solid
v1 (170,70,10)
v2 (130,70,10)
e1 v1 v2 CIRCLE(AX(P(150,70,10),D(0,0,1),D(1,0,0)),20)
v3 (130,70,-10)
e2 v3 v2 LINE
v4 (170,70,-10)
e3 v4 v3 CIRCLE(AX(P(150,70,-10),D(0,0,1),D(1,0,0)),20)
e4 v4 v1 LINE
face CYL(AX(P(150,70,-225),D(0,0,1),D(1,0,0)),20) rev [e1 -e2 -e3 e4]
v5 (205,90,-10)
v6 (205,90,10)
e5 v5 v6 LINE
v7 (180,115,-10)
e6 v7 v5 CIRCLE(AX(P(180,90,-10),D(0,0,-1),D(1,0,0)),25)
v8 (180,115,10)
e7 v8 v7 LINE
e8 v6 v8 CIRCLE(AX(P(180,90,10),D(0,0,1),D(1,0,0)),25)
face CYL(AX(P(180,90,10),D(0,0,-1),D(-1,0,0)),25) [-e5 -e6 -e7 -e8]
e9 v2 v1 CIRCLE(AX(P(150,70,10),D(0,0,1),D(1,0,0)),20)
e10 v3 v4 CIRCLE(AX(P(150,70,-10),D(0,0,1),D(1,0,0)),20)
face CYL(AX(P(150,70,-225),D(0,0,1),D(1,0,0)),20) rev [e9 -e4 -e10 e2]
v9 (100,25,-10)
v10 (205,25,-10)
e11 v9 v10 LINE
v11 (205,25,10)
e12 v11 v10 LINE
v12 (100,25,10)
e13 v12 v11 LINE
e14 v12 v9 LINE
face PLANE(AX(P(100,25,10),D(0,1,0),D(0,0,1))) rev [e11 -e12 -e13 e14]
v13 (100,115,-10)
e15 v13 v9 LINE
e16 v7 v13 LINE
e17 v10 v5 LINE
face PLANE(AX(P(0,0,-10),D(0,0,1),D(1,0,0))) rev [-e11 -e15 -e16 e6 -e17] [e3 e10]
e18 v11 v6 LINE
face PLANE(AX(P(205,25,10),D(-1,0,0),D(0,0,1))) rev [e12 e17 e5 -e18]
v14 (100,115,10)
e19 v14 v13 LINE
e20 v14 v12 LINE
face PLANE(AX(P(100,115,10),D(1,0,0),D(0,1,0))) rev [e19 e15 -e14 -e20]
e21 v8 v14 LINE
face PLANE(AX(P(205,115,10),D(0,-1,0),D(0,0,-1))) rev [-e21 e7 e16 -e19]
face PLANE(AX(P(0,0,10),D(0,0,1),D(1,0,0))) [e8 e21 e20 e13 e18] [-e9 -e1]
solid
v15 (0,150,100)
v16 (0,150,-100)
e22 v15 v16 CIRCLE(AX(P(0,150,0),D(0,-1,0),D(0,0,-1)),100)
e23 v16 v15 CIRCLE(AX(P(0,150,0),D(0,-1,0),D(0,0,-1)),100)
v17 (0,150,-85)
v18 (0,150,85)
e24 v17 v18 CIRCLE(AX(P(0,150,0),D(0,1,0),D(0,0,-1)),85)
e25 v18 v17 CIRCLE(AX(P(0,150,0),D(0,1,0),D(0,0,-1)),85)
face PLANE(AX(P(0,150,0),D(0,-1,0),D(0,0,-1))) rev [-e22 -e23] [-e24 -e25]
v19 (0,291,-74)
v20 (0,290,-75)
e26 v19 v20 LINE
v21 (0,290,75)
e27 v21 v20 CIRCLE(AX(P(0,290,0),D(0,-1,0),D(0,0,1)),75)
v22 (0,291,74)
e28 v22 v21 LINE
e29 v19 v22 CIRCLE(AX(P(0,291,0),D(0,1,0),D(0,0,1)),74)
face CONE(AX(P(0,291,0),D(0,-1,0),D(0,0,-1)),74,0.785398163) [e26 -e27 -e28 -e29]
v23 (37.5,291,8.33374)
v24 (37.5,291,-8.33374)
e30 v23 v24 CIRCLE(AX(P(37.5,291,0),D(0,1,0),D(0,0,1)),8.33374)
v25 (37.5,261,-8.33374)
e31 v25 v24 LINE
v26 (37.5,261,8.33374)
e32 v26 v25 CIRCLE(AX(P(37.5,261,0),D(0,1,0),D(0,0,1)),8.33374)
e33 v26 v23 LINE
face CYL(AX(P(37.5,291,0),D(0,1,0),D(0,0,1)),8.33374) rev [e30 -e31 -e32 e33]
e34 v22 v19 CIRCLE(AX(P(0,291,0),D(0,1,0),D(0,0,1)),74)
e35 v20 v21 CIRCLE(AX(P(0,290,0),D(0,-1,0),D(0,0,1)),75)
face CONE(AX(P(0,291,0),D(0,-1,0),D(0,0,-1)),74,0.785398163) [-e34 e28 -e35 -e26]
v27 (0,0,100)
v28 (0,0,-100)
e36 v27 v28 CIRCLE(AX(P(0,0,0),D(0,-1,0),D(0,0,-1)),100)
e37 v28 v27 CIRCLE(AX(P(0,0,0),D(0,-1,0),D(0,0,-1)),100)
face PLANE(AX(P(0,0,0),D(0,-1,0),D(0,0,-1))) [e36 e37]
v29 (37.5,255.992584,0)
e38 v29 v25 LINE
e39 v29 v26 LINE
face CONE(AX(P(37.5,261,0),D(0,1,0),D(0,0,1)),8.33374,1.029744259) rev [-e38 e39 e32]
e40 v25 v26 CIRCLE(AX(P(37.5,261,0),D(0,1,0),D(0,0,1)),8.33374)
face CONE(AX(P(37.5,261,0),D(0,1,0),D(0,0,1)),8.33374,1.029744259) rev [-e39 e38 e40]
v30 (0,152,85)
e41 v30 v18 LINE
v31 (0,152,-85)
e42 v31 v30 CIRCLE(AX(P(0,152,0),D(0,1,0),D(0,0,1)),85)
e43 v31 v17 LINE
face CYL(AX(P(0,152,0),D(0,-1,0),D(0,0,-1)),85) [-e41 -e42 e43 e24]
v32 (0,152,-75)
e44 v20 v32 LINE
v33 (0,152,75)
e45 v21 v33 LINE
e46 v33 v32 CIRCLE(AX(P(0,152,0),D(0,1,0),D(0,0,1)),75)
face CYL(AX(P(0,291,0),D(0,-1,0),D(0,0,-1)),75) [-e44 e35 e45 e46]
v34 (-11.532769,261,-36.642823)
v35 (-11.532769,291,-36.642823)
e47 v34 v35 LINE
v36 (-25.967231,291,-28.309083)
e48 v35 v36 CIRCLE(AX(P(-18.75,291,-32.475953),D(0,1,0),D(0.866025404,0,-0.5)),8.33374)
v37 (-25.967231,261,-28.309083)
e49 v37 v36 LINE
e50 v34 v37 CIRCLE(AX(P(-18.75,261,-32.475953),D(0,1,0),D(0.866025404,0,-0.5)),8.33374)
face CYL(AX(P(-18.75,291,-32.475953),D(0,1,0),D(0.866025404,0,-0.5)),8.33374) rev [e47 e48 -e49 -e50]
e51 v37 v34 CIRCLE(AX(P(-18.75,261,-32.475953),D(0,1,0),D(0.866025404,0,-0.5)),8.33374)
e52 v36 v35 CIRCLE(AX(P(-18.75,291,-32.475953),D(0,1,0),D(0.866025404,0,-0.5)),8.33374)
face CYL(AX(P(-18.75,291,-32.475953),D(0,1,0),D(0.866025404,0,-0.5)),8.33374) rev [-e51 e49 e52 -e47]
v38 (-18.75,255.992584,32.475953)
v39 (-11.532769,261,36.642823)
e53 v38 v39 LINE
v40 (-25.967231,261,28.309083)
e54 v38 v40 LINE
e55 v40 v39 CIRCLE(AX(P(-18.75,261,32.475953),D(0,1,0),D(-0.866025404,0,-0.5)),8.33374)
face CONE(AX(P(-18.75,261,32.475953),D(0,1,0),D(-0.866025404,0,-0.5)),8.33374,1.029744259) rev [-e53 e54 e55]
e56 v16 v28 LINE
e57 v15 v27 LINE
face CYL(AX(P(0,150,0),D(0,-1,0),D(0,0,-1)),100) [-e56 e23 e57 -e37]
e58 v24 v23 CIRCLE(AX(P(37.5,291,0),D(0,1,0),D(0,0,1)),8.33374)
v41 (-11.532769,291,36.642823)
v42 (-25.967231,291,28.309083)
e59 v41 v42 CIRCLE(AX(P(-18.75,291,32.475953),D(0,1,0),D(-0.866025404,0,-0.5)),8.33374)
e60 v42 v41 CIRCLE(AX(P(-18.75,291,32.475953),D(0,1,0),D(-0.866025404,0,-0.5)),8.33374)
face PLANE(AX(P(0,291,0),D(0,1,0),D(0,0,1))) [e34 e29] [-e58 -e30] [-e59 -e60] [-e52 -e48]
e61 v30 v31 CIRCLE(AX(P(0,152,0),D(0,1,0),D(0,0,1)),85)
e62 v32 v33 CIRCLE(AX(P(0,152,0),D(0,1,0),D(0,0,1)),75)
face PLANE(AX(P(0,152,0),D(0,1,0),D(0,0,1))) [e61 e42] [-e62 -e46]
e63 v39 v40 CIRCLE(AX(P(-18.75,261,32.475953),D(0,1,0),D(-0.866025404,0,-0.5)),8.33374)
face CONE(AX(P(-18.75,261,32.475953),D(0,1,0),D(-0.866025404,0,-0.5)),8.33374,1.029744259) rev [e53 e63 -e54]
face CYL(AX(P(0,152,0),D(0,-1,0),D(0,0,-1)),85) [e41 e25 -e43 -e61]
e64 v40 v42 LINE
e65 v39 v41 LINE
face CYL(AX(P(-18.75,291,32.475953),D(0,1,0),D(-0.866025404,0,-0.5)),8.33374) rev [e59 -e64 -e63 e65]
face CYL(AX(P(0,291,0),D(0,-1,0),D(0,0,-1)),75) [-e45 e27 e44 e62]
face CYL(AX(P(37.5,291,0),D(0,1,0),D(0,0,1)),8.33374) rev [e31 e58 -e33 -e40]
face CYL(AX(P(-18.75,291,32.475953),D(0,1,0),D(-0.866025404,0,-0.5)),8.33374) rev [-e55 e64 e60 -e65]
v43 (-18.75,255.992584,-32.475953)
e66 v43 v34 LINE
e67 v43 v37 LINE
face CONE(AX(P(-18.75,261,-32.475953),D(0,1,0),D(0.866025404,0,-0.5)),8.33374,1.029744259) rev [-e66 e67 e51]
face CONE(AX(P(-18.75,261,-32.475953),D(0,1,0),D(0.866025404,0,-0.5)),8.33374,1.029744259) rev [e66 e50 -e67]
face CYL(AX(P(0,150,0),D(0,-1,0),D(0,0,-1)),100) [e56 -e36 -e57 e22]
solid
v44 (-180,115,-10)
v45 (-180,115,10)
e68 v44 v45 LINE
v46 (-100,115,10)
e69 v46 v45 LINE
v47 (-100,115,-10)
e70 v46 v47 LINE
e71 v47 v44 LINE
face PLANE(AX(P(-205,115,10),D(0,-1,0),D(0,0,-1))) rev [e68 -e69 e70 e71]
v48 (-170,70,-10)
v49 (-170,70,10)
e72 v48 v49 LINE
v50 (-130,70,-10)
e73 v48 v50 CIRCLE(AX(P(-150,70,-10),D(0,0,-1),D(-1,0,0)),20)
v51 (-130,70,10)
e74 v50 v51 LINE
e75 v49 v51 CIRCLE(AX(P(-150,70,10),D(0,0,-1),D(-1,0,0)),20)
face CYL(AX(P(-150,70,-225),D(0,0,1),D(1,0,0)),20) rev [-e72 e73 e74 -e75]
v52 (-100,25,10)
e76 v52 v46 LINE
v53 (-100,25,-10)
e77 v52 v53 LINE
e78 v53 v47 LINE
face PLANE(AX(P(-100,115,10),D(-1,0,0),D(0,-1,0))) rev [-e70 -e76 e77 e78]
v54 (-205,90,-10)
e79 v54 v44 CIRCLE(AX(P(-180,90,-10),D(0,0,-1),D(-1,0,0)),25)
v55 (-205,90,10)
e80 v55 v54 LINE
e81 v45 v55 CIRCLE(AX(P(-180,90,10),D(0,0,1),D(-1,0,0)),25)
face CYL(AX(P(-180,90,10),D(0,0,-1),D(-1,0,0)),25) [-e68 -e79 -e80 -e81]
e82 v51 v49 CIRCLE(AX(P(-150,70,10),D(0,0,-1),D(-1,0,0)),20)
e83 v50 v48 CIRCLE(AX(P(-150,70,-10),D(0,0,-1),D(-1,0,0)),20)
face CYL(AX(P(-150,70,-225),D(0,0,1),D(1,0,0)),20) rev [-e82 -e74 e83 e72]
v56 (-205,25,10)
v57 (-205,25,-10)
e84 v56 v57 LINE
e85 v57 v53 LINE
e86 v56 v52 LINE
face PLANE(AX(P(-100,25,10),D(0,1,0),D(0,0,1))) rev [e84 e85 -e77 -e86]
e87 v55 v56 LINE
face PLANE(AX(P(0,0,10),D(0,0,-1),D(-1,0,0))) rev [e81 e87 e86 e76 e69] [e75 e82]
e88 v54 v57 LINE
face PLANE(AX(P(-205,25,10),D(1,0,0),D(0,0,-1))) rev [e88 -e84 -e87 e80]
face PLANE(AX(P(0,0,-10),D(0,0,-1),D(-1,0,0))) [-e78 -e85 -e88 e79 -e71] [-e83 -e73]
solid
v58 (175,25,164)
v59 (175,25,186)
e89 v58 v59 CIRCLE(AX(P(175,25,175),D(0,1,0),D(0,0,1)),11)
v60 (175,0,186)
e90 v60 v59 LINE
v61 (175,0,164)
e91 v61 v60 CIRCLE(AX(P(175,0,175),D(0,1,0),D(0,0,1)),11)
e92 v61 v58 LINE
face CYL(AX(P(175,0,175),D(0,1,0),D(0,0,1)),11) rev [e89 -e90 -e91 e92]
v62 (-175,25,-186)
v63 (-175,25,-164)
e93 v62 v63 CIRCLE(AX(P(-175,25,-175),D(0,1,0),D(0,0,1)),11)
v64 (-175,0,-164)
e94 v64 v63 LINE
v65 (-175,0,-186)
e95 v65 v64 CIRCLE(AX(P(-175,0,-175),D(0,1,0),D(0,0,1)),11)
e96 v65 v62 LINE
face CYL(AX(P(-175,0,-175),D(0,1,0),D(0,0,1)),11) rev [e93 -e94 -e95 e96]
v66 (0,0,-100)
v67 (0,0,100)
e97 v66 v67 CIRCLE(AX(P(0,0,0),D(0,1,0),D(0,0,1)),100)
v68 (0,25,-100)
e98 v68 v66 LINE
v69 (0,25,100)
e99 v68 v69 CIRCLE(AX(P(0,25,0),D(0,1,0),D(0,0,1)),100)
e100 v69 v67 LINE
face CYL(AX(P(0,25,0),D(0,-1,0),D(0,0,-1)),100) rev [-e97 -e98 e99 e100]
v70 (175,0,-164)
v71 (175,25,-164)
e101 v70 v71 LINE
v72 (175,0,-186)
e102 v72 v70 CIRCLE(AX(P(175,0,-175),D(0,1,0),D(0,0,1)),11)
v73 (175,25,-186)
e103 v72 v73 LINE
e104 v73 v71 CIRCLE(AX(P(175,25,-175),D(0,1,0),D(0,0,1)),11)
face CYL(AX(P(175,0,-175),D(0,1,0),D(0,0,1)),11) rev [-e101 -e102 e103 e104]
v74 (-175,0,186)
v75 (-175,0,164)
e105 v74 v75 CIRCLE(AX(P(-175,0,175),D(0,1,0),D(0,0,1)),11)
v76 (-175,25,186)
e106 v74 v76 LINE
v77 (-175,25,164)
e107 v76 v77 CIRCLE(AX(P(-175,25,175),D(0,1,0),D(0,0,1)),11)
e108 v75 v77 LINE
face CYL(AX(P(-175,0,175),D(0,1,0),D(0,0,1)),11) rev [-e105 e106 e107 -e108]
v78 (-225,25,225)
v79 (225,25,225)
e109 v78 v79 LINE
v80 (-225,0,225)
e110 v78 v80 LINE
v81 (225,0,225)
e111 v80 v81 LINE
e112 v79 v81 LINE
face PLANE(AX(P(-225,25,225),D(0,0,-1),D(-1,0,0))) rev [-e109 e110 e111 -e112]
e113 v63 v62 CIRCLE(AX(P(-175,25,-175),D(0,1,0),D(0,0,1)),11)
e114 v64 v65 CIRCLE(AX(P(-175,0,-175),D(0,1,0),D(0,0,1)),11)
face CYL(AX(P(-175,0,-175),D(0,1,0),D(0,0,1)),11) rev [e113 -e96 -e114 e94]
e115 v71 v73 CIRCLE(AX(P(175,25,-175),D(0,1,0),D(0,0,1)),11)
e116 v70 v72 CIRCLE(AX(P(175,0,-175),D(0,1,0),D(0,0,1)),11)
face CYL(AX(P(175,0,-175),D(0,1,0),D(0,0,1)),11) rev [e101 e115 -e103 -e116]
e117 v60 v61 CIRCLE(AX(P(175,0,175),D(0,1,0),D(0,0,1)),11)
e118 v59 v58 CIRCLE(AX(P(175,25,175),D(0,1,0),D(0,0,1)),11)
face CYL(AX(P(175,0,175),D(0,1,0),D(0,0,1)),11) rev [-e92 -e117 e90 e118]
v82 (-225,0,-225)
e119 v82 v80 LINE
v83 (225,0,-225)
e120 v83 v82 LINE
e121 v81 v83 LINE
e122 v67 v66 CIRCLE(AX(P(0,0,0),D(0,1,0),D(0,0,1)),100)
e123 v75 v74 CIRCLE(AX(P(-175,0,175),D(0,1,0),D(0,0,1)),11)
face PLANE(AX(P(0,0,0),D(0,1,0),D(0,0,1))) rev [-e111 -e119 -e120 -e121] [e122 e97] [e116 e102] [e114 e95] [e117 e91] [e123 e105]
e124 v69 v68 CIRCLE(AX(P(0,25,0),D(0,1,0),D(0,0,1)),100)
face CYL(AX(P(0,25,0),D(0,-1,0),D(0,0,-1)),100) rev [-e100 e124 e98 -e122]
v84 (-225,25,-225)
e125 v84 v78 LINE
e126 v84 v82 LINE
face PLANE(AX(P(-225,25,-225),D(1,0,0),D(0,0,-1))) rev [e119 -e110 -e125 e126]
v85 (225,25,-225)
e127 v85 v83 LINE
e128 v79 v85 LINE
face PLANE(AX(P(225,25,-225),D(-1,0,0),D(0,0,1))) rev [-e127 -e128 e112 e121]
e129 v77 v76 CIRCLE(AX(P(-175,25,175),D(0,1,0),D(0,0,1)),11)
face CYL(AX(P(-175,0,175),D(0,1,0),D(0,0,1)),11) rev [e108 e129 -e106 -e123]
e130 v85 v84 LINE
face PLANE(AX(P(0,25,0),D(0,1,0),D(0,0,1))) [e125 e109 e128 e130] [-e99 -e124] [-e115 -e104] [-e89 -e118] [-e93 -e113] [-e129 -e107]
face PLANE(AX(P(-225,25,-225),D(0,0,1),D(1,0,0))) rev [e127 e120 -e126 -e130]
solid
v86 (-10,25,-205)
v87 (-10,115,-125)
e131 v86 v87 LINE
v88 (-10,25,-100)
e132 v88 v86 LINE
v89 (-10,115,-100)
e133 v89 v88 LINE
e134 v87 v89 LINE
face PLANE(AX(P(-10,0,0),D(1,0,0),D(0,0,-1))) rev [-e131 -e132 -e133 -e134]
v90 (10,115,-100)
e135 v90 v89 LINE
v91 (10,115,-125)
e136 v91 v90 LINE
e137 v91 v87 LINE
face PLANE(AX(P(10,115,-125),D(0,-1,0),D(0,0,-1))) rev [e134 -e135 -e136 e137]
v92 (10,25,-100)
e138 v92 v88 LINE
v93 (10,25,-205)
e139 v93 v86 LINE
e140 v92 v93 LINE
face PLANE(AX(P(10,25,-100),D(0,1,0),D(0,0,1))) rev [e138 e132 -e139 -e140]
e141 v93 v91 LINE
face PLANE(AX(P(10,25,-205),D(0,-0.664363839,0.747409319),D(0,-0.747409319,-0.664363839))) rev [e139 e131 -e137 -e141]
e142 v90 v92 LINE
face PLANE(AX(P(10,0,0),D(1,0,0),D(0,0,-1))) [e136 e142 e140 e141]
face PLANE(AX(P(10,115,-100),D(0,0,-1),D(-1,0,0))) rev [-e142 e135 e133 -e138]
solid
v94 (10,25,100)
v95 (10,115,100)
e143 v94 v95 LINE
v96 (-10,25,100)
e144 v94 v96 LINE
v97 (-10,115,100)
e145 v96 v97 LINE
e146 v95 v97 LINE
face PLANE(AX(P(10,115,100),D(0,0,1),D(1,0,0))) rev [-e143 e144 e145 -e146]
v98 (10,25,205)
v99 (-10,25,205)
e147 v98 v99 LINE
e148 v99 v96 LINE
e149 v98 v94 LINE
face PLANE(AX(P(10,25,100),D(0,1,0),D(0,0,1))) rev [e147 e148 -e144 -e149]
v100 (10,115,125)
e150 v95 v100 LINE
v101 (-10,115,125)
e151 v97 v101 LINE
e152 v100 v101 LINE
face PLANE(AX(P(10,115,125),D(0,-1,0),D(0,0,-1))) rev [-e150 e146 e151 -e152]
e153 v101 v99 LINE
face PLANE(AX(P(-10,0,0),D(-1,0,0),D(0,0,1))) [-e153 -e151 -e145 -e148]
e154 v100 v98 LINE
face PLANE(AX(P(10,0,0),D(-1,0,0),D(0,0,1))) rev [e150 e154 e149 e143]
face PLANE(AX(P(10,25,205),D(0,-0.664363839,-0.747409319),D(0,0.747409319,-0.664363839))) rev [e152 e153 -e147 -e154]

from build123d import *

# Parameters (mm, degrees)
SKETCH1_W               = 450
SKETCH1_H               = 450
SKETCH1_R               = 100
BOSS_EXTRUDE1_DEPTH     = 25
SKETCH2_R               = 100
BOSS_EXTRUDE2_DEPTH     = 150
SKETCH3_R               = 85
BOSS_EXTRUDE3_DEPTH     = 2
SKETCH4_R               = 75
BOSS_EXTRUDE4_DEPTH     = 139
SKETCH5_R               = 11
CUT_EXTRUDE1_DEPTH      = 415.736060646
CIRPATTERN1_COUNT       = 3
CHAMFER1_SIZE           = 1
SKETCH8_W               = 105
SKETCH8_H               = 90
BOSS_EXTRUDE5_DEPTH     = 10
BOSS_EXTRUDE5_2_DEPTH   = 10
FILLET1_R               = 25
FILLET2_R               = 25
CUT_EXTRUDE2_DEPTH      = 437.498568153
CUT_EXTRUDE2_DEPTH_BACK = 437.498568153
SKETCH9_R               = 20
BOSS_EXTRUDE6_DEPTH     = 10
BOSS_EXTRUDE6_2_DEPTH   = 10


with BuildPart() as part:
    # Sketch1 → Boss-Extrude1 (new body)
    with BuildSketch(Plane(origin=(0, 0, 0), x_dir=(1, 0, 0), z_dir=(0, 1, 0))):
        Rectangle(SKETCH1_W, SKETCH1_H)
        with Locations(Location((0, 0, 0), (0, 0, 270))):
            Circle(SKETCH1_R, mode=Mode.SUBTRACT)
    extrude(amount=BOSS_EXTRUDE1_DEPTH)

    # Sketch5 → Cut-Extrude1 (cut, through all)
    with BuildSketch(Plane(origin=(0, 25, 0), x_dir=(1, 0, 0), z_dir=(0, 1, 0))):
        with Locations(Location((-175, 175, 0), (0, 0, 270))):
            Circle(SKETCH5_R)
        with Locations(Location((175, 175, 0), (0, 0, 270))):
            Circle(SKETCH5_R)
        with Locations(Location((175, -175, 0), (0, 0, 270))):
            Circle(SKETCH5_R)
        with Locations(Location((-175, -175, 0), (0, 0, 270))):
            Circle(SKETCH5_R)
    extrude(amount=-CUT_EXTRUDE1_DEPTH, mode=Mode.SUBTRACT)


with BuildPart() as body_2:
    # Sketch2 → Boss-Extrude2 (new body)
    with BuildSketch(Plane.XZ):
        with Locations(Location((0, 0, 0), (0, 0, 270))):
            Circle(SKETCH2_R)
    extrude(amount=-BOSS_EXTRUDE2_DEPTH)

    # Sketch3 → Boss-Extrude3 (add)
    with BuildSketch(Plane(origin=(0, 150, 0), x_dir=(1, 0, 0), z_dir=(0, 1, 0))):
        with Locations(Location((0, 0, 0), (0, 0, 90))):
            Circle(SKETCH3_R)
    extrude(amount=BOSS_EXTRUDE3_DEPTH)

    # Sketch4 → Boss-Extrude4 (add)
    with BuildSketch(Plane(origin=(0, 152, 0), x_dir=(1, 0, 0), z_dir=(0, 1, 0))):
        with Locations(Location((0, 0, 0), (0, 0, 270))):
            Circle(SKETCH4_R)
    extrude(amount=BOSS_EXTRUDE4_DEPTH)

    # Sketch7 → 3/4-10 Tapped Hole1 (revolve, cut)
    with BuildSketch(Plane(origin=(37.5, 291, 0), x_dir=(0, 0, 1), z_dir=(1, 0, 0))):
        Polygon((0, 0), (0, 35.007416175), (8.33374, 30), (8.33374, 0), align=None)
    f_3_4_10_tapped_hole1 = revolve(axis=Axis((37.5, 297.35, 0), (0, -1, 0)), mode=Mode.SUBTRACT)

    # CirPattern1: 3/4-10 Tapped Hole1 ×3 about axis
    cirpattern1_axis = Axis((0, 0, 0), (0, 1, 0))
    for i in range(1, CIRPATTERN1_COUNT):
        add(f_3_4_10_tapped_hole1.rotate(cirpattern1_axis, i * 360 / CIRPATTERN1_COUNT), mode=Mode.SUBTRACT)

    # Chamfer1
    chamfer1_edges = [body_2.edges().sort_by_distance(p)[0] for p in [
        (0, 291, -75),
    ]]
    chamfer(chamfer1_edges, length=CHAMFER1_SIZE)


with BuildPart() as body_3:
    # Sketch8 → Boss-Extrude5 (new, symmetric)
    with BuildSketch(Plane.XY):
        with Locations((-152.5, 70)):
            Rectangle(SKETCH8_W, SKETCH8_H)
    extrude(amount=BOSS_EXTRUDE5_DEPTH, both=True)

    # Fillet1
    fillet1_edges = [body_3.edges().sort_by_distance(p)[0] for p in [
        (-205, 115, 0),
    ]]
    fillet(fillet1_edges, radius=FILLET1_R)


with BuildPart() as body_4:
    # Sketch8 → Boss-Extrude5 2 (new, symmetric)
    with BuildSketch(Plane.XY):
        with Locations((152.5, 70)):
            Rectangle(SKETCH8_W, SKETCH8_H)
    extrude(amount=BOSS_EXTRUDE5_2_DEPTH, both=True)

    # Fillet2
    fillet2_edges = [body_4.edges().sort_by_distance(p)[0] for p in [
        (205, 115, 0),
    ]]
    fillet(fillet2_edges, radius=FILLET2_R)


with BuildPart() as cut_extrude2_tool:
    # Sketch9 → Cut-Extrude2 (new, two sides: drawn at the far end of the back side and taken through both)
    with BuildSketch(Plane.XY.offset(10).offset(-CUT_EXTRUDE2_DEPTH_BACK)):
        with Locations(Location((-150, 70, 0), (0, 0, 180))):
            Circle(SKETCH9_R)
        with Locations((150, 70)):
            Circle(SKETCH9_R)
    extrude(amount=CUT_EXTRUDE2_DEPTH + CUT_EXTRUDE2_DEPTH_BACK)


with BuildPart() as body_3_1:
    add(body_3.part)

    # Cut-Extrude2: cut by cut_extrude2_tool
    add(cut_extrude2_tool.part, mode=Mode.SUBTRACT)


with BuildPart() as body_4_1:
    add(body_4.part)

    # Cut-Extrude2: cut by cut_extrude2_tool
    add(cut_extrude2_tool.part, mode=Mode.SUBTRACT)


with BuildPart() as body_5:
    # Sketch10 → Boss-Extrude6 (new, symmetric)
    with BuildSketch(Plane(origin=(0, 0, 0), x_dir=(0, 0, -1), z_dir=(1, 0, 0))):
        Polygon((-100, 25), (-205, 25), (-125, 115), (-100, 115), align=None)
    extrude(amount=BOSS_EXTRUDE6_DEPTH, both=True)


with BuildPart() as body_6:
    # Sketch10 → Boss-Extrude6 2 (new, symmetric)
    with BuildSketch(Plane(origin=(0, 0, 0), x_dir=(0, 0, -1), z_dir=(1, 0, 0))):
        Polygon((100, 115), (100, 25), (205, 25), (125, 115), align=None)
    extrude(amount=BOSS_EXTRUDE6_2_DEPTH, both=True)


solid = Compound([part.part, body_2.part, body_3_1.part, body_4_1.part, body_5.part, body_6.part])
